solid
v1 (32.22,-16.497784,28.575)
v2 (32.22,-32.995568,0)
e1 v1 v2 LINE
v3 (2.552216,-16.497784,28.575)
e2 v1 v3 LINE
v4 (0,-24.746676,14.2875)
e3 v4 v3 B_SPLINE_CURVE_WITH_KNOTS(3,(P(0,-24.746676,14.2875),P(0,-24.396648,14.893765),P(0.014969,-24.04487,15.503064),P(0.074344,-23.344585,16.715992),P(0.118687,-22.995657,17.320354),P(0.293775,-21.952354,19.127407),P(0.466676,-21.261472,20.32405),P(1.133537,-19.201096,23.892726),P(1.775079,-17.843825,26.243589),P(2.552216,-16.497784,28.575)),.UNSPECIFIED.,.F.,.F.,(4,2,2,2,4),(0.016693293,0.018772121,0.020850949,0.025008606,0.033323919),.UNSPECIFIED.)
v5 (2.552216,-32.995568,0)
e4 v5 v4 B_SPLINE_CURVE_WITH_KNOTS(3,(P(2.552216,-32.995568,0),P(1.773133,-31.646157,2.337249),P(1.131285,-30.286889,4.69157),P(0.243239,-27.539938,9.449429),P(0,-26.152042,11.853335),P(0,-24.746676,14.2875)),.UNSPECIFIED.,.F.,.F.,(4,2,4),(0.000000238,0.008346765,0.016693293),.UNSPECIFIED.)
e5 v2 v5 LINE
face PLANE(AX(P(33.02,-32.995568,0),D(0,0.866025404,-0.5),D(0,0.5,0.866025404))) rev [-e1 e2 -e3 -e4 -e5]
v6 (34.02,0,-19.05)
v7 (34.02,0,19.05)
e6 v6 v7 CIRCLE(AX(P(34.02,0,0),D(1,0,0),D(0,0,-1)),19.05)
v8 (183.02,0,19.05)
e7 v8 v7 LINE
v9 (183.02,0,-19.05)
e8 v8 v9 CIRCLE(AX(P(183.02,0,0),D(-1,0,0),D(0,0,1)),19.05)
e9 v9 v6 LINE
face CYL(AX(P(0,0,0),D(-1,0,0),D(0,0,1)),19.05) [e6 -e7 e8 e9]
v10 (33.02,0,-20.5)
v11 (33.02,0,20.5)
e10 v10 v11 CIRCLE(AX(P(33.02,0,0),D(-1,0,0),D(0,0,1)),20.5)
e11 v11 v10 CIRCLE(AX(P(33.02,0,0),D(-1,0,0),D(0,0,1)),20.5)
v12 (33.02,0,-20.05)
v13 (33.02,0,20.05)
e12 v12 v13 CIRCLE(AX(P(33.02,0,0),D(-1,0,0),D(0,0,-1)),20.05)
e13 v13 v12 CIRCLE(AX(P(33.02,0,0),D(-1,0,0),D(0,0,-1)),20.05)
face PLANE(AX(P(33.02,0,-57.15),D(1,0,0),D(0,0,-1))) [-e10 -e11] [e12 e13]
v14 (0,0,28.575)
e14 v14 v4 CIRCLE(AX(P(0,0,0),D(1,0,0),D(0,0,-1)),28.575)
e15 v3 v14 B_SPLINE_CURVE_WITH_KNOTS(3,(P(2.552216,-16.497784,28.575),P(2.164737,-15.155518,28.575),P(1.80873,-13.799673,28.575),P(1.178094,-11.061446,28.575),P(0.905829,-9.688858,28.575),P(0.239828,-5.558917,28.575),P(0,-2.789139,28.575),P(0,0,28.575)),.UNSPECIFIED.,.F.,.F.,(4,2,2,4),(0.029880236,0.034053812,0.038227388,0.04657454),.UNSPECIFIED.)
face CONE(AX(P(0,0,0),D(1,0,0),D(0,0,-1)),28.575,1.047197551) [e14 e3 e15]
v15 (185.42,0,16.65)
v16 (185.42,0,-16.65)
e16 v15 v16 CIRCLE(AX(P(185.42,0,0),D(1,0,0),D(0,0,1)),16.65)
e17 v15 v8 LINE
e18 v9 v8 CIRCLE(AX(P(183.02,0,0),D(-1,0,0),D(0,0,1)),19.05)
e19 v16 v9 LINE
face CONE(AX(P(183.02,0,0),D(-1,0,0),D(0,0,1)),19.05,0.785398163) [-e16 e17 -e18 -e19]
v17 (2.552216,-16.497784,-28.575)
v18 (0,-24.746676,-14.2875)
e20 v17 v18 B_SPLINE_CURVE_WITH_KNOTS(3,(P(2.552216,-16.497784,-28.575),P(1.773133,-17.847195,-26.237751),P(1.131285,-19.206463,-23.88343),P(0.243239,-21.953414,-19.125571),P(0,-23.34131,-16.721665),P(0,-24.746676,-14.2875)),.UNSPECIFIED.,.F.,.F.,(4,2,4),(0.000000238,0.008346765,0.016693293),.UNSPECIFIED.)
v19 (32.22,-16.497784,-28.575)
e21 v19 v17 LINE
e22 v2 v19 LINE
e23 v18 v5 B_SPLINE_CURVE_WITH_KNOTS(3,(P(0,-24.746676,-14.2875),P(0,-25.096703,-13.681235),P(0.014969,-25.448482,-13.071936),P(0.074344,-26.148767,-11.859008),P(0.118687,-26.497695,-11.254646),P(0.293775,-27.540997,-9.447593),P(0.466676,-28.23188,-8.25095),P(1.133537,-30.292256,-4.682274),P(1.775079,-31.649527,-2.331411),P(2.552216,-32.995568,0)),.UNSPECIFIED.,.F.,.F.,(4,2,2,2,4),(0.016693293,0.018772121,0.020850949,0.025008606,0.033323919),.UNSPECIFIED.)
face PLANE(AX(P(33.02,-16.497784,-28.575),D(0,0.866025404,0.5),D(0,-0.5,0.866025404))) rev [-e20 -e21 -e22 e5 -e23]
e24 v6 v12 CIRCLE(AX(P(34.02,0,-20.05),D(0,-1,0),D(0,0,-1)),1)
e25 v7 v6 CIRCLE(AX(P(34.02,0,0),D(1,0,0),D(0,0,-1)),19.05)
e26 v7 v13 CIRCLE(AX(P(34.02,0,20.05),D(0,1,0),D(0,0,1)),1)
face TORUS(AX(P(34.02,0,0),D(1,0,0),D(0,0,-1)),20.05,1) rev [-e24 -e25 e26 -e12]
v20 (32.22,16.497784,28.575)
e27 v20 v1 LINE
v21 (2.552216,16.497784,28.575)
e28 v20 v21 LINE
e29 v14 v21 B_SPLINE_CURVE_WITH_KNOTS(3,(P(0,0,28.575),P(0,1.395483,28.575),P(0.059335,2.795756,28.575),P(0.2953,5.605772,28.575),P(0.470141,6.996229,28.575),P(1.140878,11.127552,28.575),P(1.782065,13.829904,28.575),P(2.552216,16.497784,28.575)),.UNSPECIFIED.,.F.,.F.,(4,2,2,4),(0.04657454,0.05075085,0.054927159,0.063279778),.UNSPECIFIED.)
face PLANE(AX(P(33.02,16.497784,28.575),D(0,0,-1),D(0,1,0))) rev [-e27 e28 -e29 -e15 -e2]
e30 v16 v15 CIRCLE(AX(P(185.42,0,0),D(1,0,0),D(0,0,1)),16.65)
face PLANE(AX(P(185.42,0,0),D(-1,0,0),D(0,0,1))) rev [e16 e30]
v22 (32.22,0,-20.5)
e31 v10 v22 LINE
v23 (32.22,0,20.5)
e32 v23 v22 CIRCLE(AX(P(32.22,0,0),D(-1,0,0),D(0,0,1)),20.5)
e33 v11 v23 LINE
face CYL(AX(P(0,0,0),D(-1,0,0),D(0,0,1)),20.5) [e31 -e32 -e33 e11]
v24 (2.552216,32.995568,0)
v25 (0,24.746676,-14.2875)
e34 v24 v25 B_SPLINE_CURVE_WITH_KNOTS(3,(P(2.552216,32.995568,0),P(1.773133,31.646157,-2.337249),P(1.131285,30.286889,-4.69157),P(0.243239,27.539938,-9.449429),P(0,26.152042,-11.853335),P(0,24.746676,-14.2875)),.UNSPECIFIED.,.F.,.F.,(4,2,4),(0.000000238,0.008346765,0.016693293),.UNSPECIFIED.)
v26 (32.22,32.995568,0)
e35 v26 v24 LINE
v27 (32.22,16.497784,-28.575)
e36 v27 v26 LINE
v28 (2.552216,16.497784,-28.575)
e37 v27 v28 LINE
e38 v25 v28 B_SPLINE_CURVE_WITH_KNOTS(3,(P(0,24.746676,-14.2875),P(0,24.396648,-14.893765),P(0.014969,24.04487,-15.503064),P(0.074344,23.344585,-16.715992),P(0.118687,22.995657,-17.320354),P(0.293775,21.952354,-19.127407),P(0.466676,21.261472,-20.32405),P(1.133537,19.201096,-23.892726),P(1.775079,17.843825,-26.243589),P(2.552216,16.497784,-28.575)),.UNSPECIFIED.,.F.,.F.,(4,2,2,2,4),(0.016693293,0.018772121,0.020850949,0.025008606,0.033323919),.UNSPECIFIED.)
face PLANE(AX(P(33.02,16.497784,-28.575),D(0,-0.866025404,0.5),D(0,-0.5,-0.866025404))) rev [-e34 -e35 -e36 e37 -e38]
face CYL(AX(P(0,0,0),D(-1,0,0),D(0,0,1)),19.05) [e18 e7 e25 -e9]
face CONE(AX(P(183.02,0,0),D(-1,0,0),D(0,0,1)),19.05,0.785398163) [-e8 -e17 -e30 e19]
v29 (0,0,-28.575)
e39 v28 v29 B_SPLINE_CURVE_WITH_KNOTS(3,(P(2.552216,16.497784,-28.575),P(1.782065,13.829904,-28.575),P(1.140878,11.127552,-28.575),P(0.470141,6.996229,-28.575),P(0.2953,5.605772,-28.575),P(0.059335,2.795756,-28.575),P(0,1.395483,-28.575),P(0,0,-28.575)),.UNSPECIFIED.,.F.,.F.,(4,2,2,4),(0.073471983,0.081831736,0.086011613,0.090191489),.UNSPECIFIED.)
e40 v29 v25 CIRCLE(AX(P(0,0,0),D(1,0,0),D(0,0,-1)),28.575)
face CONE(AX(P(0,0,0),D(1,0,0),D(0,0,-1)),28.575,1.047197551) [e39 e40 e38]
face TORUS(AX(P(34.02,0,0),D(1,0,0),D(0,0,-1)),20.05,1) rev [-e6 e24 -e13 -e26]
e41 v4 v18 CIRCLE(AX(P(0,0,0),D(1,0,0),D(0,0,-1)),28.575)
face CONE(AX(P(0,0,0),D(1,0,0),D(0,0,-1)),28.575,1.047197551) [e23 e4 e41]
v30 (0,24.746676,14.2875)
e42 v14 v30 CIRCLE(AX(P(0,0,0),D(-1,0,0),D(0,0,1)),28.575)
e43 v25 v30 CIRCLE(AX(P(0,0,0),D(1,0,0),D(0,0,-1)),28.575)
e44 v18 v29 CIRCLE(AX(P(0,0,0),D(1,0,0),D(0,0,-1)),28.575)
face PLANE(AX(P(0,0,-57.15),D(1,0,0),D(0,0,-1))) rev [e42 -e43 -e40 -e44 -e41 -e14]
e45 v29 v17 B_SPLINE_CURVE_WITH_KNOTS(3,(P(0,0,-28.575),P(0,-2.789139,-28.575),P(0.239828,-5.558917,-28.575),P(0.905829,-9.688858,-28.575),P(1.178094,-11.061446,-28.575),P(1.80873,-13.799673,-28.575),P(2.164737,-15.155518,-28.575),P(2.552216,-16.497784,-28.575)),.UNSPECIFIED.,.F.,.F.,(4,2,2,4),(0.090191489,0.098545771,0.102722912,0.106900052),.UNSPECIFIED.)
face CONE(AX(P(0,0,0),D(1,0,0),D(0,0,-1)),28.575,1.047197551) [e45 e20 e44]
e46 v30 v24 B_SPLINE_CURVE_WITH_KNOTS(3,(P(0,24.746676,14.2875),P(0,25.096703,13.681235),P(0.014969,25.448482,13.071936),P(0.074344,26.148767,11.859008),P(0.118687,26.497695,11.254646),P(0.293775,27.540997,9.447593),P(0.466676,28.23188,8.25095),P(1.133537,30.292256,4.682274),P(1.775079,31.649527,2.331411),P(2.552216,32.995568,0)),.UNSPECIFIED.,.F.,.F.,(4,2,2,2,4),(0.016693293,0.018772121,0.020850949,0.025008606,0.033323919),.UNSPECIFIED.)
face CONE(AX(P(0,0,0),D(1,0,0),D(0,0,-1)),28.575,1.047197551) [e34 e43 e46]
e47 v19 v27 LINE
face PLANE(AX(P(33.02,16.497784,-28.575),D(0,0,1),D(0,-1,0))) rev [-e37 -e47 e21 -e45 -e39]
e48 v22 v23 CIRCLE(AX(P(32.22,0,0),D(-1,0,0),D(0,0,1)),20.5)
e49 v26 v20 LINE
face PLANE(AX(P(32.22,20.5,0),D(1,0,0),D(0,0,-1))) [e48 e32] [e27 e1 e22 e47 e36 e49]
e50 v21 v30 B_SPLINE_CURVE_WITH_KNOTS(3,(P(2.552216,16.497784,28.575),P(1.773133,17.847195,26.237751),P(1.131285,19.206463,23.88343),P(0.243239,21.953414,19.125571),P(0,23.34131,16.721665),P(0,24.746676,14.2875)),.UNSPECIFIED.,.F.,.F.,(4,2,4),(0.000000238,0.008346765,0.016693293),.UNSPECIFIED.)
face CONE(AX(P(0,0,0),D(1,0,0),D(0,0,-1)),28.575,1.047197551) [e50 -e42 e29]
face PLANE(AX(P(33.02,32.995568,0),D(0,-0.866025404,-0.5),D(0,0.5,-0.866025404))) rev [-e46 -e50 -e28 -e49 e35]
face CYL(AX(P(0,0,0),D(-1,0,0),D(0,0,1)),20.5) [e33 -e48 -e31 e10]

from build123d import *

# Parameters (mm, degrees)
BASE_EXTRUDE_DEPTH = 33.02
SKETCH4_W          = 0.8
SKETCH4_H          = 22.495567884
CHAMFER_2_SIZE     = 2.4
FILLET_2_R         = 1


with BuildPart() as part:
    # Sketch1 → Base-Extrude (new body)
    with BuildSketch(Plane(origin=(0, 0, 0), x_dir=(0, 0, -1), z_dir=(1, 0, 0))):
        Polygon((28.575, 16.497783942), (28.575, -16.497783942), (0, -32.995567884), (-28.575, -16.497783942), (-28.575, 16.497783942), (0, 32.995567884), align=None)
    extrude(amount=BASE_EXTRUDE_DEPTH)

    # Sketch2 → Boss-Revolve1 (revolve)
    with BuildSketch(Plane.XY, mode=Mode.PRIVATE) as boss_revolve1_sk:
        Polygon((0, 0), (185.42, 0), (185.42, 13.8), (185.42, 19.05), (27.8072, 19.05), (0, 19.05), align=None)
    revolve(boss_revolve1_sk.sketch.rotate(Axis((0, 0, 0), (1, 0, 0)), 90), axis=Axis((0, 0, 0), (1, 0, 0)))

    # Sketch3 → Cut-Revolve1 (revolve, cut)
    with BuildSketch(Plane.XY):
        Polygon((0, 28.575), (5.438967404, 37.995567884), (5.438967404, 42.995567884), (-10, 42.995567884), (-10, 28.575), align=None)
    revolve(axis=Axis((0, 0, 0), (1, 0, 0)), mode=Mode.SUBTRACT)

    # Sketch4 → Cut-Revolve3 (revolve, cut)
    with BuildSketch(Plane.XY, mode=Mode.PRIVATE) as cut_revolve3_sk:
        with Locations((32.62, 31.747783942)):
            Rectangle(SKETCH4_W, SKETCH4_H)
    revolve(cut_revolve3_sk.sketch.rotate(Axis((0, 0, 0), (1, 0, 0)), 90), axis=Axis((0, 0, 0), (1, 0, 0)), mode=Mode.SUBTRACT)

    # Chamfer 2
    chamfer_2_edges = [part.edges().sort_by_distance(p)[0] for p in [
        (185.42, 0, -19.05),
    ]]
    chamfer(chamfer_2_edges, length=CHAMFER_2_SIZE)

    # Fillet 2
    fillet_2_edges = [part.edges().sort_by_distance(p)[0] for p in [
        (33.02, 0, -19.05),
    ]]
    fillet(fillet_2_edges, radius=FILLET_2_R)


solid = part.part
